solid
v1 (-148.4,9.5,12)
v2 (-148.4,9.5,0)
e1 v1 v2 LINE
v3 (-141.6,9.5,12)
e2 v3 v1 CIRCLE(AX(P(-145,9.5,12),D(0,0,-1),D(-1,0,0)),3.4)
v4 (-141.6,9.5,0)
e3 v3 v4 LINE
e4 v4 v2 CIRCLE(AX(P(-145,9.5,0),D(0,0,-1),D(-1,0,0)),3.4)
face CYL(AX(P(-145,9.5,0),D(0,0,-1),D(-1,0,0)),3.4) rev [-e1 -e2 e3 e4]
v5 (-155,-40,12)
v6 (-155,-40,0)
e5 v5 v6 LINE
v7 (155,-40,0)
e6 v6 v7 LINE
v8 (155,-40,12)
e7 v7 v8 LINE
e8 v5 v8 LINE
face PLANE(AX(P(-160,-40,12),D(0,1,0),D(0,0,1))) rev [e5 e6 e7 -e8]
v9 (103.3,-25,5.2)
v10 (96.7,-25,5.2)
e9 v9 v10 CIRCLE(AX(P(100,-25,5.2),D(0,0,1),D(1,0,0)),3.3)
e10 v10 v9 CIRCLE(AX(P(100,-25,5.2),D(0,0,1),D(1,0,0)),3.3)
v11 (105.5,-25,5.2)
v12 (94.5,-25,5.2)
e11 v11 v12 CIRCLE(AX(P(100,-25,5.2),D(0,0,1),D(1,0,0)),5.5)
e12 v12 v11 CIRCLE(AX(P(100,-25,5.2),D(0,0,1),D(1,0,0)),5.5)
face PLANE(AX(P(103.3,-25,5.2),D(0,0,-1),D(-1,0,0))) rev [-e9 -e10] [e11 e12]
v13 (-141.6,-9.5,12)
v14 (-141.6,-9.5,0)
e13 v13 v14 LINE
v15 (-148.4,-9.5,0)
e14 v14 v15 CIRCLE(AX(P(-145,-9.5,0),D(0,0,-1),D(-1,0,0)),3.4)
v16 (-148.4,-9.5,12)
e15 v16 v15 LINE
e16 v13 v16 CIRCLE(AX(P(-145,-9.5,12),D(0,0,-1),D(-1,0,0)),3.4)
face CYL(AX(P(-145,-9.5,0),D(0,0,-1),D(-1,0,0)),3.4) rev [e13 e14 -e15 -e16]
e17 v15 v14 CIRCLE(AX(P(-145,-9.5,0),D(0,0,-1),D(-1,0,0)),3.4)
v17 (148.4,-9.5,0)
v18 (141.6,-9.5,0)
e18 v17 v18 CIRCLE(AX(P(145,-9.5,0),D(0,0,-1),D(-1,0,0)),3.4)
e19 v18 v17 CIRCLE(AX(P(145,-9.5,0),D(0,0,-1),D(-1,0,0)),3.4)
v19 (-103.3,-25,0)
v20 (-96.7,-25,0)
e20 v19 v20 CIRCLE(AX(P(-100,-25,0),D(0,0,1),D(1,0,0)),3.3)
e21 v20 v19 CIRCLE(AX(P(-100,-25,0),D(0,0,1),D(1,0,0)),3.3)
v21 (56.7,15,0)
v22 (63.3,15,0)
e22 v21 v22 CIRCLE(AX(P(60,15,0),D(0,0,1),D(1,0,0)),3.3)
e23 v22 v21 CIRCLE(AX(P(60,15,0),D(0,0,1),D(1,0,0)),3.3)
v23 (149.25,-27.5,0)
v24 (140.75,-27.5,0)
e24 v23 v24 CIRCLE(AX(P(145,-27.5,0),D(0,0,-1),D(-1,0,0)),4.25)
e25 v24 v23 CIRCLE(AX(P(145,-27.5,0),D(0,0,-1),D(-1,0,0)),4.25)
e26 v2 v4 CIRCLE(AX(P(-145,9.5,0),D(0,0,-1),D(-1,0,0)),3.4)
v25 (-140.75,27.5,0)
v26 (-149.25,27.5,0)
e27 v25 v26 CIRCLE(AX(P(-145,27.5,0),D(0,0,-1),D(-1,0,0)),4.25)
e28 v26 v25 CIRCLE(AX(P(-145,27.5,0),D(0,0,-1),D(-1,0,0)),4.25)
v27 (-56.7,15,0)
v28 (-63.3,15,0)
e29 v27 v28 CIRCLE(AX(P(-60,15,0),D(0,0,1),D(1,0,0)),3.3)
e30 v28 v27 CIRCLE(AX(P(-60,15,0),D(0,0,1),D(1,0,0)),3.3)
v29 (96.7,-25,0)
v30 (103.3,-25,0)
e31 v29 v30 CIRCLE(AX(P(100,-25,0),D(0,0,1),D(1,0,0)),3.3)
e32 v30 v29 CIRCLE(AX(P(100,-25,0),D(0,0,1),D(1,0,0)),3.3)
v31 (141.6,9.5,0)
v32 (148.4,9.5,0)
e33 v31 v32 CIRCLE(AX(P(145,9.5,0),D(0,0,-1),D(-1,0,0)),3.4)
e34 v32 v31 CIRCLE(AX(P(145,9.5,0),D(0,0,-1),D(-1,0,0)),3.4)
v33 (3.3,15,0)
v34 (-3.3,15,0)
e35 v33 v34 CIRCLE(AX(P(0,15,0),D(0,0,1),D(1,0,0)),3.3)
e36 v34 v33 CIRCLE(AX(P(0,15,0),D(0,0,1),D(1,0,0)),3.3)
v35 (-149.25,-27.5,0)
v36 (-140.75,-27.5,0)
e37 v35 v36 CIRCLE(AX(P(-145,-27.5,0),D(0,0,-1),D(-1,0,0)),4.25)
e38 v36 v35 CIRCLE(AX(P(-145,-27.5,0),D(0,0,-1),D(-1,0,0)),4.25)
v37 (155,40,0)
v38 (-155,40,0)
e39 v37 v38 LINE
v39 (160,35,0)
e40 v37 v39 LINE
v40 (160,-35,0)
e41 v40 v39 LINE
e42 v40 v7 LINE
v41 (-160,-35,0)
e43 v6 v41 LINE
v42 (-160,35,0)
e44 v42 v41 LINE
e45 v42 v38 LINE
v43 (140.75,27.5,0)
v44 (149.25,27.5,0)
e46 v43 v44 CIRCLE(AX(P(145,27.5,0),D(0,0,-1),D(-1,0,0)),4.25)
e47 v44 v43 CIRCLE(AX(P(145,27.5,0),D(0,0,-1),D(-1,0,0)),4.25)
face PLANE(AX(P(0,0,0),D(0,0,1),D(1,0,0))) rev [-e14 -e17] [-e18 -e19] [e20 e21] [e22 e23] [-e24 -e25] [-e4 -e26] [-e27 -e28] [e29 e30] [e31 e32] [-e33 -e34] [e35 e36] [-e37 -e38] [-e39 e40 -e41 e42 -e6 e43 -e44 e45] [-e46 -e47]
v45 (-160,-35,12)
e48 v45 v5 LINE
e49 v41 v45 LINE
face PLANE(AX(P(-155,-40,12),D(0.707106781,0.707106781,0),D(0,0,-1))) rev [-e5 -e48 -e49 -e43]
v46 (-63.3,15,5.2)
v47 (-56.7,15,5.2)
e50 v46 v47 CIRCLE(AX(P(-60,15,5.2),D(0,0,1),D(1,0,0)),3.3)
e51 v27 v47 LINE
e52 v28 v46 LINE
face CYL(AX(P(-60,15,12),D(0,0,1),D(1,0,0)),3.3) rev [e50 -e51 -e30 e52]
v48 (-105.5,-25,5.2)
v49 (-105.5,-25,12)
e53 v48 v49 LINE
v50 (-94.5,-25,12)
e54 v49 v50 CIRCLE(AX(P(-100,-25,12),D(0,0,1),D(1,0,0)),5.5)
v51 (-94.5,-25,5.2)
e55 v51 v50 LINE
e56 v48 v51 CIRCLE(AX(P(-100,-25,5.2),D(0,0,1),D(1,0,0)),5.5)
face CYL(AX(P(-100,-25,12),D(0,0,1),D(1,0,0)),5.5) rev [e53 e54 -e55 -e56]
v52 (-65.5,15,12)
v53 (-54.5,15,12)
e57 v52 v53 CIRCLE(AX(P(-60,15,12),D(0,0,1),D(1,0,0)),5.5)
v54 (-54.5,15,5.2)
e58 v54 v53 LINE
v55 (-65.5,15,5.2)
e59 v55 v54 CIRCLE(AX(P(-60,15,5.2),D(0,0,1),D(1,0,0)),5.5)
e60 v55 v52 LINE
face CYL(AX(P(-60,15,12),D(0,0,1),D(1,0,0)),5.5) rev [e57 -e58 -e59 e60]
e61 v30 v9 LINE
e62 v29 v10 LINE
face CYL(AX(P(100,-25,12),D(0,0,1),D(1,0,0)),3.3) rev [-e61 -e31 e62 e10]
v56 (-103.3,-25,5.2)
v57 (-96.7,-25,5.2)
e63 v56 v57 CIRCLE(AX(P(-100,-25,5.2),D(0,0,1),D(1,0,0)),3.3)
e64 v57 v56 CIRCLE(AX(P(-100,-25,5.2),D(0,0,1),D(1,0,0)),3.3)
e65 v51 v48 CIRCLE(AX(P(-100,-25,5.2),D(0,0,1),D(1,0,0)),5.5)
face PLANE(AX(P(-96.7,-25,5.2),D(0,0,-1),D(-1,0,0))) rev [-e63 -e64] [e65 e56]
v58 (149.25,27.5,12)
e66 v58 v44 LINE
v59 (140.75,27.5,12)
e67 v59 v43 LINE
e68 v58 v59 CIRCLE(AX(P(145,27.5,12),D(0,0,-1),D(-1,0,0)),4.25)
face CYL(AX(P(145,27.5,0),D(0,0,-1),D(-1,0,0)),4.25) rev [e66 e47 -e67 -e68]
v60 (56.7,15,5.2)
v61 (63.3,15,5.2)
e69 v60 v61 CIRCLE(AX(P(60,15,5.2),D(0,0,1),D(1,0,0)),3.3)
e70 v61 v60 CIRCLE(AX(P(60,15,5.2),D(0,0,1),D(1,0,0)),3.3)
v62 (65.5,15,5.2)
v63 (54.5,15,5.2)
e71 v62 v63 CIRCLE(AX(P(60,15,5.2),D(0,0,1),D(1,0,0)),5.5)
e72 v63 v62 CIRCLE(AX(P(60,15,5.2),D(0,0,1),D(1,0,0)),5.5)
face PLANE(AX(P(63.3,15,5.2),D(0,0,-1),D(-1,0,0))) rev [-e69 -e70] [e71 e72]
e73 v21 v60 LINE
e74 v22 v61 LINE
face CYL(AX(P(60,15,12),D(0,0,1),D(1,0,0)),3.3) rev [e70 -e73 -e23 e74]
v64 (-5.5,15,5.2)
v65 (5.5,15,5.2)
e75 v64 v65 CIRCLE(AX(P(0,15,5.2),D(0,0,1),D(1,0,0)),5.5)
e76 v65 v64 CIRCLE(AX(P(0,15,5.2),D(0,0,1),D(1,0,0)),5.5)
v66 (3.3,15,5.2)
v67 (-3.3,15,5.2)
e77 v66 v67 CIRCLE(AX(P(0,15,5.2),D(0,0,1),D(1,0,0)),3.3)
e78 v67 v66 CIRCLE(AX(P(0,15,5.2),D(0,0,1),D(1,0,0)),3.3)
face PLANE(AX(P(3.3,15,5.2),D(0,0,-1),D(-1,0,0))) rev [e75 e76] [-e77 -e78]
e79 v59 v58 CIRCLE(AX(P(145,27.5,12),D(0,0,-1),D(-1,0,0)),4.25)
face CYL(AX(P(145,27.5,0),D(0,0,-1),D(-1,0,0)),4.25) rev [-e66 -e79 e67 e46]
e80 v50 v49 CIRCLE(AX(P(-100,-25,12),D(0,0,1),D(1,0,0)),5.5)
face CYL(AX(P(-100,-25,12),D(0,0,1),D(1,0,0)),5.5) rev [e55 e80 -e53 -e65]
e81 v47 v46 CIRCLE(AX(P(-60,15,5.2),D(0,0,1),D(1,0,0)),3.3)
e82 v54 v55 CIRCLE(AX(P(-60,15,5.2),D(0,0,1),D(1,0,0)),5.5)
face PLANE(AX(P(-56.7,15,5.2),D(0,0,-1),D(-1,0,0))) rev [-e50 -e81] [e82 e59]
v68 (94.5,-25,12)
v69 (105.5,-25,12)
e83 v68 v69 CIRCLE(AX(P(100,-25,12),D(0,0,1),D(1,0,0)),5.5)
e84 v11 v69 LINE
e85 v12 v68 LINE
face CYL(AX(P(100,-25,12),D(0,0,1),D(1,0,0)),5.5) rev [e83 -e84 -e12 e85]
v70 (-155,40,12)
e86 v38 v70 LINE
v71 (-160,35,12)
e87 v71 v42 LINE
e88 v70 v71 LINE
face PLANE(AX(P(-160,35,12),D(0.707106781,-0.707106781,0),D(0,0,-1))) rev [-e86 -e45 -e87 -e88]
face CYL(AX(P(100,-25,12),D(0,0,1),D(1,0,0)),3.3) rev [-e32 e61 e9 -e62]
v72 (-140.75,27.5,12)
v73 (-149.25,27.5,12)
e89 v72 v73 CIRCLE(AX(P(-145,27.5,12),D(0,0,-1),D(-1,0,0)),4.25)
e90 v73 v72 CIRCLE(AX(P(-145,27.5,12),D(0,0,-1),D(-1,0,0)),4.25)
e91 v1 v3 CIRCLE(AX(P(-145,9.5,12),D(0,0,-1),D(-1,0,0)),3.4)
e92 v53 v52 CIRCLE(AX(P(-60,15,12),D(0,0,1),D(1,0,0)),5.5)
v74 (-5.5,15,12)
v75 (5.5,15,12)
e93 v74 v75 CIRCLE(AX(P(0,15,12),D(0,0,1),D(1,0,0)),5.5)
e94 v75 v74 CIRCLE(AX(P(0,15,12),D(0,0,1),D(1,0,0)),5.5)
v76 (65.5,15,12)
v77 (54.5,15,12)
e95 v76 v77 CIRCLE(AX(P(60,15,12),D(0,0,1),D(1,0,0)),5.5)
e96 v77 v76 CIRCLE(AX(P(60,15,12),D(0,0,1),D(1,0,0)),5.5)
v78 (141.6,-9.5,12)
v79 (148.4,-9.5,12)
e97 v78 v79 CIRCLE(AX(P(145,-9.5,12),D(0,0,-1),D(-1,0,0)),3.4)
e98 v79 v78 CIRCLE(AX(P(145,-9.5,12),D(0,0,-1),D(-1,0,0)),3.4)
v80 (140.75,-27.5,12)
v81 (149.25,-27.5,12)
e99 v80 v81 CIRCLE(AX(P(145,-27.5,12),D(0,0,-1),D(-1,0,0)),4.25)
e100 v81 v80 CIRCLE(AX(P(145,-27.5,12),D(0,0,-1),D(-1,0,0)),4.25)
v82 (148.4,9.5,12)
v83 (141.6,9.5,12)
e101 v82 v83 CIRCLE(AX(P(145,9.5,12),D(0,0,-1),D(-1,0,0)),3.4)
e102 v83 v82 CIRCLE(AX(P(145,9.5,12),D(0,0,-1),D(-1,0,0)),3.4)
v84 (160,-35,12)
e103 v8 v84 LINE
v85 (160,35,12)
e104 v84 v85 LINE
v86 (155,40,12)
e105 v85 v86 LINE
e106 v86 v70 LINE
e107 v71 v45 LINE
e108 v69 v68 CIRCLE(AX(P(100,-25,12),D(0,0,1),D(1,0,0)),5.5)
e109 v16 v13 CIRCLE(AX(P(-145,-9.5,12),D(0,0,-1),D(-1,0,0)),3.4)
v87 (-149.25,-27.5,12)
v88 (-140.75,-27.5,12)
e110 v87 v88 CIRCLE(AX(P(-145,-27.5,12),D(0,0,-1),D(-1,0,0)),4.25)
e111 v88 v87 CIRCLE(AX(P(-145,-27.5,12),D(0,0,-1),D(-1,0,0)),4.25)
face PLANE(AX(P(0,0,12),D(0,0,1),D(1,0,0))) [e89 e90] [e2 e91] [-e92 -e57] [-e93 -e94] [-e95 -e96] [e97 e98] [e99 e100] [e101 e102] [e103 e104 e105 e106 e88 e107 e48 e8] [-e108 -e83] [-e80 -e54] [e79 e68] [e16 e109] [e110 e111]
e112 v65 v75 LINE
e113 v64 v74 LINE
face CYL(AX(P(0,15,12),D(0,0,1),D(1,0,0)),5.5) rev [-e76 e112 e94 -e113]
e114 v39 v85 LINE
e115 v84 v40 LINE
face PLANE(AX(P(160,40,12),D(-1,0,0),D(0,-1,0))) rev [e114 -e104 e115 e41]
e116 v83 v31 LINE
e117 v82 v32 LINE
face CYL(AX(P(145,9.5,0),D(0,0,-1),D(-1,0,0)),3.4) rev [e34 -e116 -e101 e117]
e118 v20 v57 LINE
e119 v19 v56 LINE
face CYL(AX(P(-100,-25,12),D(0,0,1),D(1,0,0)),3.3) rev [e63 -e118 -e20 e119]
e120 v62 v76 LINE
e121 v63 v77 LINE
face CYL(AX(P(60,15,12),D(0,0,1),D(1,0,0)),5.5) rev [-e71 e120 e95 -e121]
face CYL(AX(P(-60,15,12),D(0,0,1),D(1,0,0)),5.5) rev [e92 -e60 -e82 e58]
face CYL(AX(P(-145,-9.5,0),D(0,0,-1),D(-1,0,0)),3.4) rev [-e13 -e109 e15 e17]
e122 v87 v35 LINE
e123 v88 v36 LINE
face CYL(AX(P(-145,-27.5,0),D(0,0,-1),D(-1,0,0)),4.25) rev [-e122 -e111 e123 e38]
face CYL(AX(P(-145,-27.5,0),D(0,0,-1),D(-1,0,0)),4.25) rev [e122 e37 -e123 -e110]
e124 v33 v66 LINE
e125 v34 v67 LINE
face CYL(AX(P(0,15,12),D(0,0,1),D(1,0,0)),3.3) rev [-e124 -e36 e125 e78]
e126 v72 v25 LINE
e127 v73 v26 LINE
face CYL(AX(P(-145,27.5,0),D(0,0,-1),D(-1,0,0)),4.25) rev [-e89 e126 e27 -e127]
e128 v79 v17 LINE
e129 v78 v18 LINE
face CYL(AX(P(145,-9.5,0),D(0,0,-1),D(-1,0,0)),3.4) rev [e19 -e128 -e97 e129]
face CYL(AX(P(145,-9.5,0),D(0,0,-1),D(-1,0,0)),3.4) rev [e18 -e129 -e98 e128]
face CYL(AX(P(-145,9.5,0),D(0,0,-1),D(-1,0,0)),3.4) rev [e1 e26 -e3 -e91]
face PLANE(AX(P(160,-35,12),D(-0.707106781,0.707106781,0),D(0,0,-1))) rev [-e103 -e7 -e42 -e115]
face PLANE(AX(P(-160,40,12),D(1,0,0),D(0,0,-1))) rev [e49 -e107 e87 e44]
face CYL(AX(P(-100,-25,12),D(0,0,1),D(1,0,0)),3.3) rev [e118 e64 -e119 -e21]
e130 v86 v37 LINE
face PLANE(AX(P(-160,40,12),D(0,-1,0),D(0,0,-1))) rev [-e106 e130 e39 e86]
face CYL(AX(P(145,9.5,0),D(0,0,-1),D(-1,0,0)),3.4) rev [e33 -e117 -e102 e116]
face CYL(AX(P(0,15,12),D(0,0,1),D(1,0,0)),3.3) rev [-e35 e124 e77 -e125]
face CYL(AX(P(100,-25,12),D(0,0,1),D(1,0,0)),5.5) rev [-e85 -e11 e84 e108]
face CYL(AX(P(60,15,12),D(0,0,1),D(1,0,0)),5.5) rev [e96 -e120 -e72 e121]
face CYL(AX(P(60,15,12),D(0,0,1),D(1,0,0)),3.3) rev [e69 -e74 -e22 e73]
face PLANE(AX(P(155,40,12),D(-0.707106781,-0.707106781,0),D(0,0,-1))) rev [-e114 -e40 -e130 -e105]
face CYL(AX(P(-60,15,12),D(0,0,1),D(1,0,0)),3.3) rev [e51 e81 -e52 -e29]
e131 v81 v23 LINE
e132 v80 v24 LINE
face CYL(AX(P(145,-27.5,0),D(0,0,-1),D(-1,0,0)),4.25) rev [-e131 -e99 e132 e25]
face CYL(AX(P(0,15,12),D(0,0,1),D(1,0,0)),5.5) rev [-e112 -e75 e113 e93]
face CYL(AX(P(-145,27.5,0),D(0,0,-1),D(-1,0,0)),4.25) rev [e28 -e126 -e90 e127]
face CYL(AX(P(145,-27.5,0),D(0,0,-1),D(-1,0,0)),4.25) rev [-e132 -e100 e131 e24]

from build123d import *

# Parameters (mm, degrees)
SKETCH_1_W                = 320
SKETCH_1_H                = 80
EXTRUDE_1_DEPTH           = 12
CHAMFER_1_SIZE            = 5
HOLE_WIZARD_M8_1_D        = 6.8
HOLE_WIZARD_8_5_8_5_1_D   = 8.5
HOLE_WIZARD_1_D           = 6.6
HOLE_WIZARD_1_CBORE_D     = 11
HOLE_WIZARD_1_CBORE_DEPTH = 6.8


with BuildPart() as part:
    # 草图1 → 凸台-拉伸1 (new body)
    with BuildSketch(Plane.XY):
        Rectangle(SKETCH_1_W, SKETCH_1_H)
    extrude(amount=EXTRUDE_1_DEPTH)

    # 倒角1
    chamfer_1_edges = [part.edges().sort_by_distance(p)[0] for p in [
        (160, -40, 6),
        (-160, -40, 6),
        (-160, 40, 6),
        (160, 40, 6),
    ]]
    chamfer(chamfer_1_edges, length=CHAMFER_1_SIZE)

    # M8 螺纹孔1 (through all)
    with Locations(Plane(origin=(0, 0, 0), x_dir=(-1, 0, 0), z_dir=(0, 0, -1))):
        with Locations((-145, 9.5), (-145, -9.5), (145, 9.5), (145, -9.5)):
            Hole(HOLE_WIZARD_M8_1_D / 2)

    # Ø8.5 (8.5) 直径孔1 (through all)
    with Locations(Plane(origin=(0, 0, 0), x_dir=(-1, 0, 0), z_dir=(0, 0, -1))):
        with Locations((-145, 27.5), (-145, -27.5), (145, 27.5), (145, -27.5)):
            Hole(HOLE_WIZARD_8_5_8_5_1_D / 2)

    # 打孔尺寸(%根据)内六角圆柱头螺钉的类型1 (through all)
    with Locations(Plane.XY.offset(12)):
        with Locations((-60, 15), (0, 15), (60, 15), (100, -25), (-100, -25)):
            CounterBoreHole(HOLE_WIZARD_1_D / 2, HOLE_WIZARD_1_CBORE_D / 2, HOLE_WIZARD_1_CBORE_DEPTH)


solid = part.part
